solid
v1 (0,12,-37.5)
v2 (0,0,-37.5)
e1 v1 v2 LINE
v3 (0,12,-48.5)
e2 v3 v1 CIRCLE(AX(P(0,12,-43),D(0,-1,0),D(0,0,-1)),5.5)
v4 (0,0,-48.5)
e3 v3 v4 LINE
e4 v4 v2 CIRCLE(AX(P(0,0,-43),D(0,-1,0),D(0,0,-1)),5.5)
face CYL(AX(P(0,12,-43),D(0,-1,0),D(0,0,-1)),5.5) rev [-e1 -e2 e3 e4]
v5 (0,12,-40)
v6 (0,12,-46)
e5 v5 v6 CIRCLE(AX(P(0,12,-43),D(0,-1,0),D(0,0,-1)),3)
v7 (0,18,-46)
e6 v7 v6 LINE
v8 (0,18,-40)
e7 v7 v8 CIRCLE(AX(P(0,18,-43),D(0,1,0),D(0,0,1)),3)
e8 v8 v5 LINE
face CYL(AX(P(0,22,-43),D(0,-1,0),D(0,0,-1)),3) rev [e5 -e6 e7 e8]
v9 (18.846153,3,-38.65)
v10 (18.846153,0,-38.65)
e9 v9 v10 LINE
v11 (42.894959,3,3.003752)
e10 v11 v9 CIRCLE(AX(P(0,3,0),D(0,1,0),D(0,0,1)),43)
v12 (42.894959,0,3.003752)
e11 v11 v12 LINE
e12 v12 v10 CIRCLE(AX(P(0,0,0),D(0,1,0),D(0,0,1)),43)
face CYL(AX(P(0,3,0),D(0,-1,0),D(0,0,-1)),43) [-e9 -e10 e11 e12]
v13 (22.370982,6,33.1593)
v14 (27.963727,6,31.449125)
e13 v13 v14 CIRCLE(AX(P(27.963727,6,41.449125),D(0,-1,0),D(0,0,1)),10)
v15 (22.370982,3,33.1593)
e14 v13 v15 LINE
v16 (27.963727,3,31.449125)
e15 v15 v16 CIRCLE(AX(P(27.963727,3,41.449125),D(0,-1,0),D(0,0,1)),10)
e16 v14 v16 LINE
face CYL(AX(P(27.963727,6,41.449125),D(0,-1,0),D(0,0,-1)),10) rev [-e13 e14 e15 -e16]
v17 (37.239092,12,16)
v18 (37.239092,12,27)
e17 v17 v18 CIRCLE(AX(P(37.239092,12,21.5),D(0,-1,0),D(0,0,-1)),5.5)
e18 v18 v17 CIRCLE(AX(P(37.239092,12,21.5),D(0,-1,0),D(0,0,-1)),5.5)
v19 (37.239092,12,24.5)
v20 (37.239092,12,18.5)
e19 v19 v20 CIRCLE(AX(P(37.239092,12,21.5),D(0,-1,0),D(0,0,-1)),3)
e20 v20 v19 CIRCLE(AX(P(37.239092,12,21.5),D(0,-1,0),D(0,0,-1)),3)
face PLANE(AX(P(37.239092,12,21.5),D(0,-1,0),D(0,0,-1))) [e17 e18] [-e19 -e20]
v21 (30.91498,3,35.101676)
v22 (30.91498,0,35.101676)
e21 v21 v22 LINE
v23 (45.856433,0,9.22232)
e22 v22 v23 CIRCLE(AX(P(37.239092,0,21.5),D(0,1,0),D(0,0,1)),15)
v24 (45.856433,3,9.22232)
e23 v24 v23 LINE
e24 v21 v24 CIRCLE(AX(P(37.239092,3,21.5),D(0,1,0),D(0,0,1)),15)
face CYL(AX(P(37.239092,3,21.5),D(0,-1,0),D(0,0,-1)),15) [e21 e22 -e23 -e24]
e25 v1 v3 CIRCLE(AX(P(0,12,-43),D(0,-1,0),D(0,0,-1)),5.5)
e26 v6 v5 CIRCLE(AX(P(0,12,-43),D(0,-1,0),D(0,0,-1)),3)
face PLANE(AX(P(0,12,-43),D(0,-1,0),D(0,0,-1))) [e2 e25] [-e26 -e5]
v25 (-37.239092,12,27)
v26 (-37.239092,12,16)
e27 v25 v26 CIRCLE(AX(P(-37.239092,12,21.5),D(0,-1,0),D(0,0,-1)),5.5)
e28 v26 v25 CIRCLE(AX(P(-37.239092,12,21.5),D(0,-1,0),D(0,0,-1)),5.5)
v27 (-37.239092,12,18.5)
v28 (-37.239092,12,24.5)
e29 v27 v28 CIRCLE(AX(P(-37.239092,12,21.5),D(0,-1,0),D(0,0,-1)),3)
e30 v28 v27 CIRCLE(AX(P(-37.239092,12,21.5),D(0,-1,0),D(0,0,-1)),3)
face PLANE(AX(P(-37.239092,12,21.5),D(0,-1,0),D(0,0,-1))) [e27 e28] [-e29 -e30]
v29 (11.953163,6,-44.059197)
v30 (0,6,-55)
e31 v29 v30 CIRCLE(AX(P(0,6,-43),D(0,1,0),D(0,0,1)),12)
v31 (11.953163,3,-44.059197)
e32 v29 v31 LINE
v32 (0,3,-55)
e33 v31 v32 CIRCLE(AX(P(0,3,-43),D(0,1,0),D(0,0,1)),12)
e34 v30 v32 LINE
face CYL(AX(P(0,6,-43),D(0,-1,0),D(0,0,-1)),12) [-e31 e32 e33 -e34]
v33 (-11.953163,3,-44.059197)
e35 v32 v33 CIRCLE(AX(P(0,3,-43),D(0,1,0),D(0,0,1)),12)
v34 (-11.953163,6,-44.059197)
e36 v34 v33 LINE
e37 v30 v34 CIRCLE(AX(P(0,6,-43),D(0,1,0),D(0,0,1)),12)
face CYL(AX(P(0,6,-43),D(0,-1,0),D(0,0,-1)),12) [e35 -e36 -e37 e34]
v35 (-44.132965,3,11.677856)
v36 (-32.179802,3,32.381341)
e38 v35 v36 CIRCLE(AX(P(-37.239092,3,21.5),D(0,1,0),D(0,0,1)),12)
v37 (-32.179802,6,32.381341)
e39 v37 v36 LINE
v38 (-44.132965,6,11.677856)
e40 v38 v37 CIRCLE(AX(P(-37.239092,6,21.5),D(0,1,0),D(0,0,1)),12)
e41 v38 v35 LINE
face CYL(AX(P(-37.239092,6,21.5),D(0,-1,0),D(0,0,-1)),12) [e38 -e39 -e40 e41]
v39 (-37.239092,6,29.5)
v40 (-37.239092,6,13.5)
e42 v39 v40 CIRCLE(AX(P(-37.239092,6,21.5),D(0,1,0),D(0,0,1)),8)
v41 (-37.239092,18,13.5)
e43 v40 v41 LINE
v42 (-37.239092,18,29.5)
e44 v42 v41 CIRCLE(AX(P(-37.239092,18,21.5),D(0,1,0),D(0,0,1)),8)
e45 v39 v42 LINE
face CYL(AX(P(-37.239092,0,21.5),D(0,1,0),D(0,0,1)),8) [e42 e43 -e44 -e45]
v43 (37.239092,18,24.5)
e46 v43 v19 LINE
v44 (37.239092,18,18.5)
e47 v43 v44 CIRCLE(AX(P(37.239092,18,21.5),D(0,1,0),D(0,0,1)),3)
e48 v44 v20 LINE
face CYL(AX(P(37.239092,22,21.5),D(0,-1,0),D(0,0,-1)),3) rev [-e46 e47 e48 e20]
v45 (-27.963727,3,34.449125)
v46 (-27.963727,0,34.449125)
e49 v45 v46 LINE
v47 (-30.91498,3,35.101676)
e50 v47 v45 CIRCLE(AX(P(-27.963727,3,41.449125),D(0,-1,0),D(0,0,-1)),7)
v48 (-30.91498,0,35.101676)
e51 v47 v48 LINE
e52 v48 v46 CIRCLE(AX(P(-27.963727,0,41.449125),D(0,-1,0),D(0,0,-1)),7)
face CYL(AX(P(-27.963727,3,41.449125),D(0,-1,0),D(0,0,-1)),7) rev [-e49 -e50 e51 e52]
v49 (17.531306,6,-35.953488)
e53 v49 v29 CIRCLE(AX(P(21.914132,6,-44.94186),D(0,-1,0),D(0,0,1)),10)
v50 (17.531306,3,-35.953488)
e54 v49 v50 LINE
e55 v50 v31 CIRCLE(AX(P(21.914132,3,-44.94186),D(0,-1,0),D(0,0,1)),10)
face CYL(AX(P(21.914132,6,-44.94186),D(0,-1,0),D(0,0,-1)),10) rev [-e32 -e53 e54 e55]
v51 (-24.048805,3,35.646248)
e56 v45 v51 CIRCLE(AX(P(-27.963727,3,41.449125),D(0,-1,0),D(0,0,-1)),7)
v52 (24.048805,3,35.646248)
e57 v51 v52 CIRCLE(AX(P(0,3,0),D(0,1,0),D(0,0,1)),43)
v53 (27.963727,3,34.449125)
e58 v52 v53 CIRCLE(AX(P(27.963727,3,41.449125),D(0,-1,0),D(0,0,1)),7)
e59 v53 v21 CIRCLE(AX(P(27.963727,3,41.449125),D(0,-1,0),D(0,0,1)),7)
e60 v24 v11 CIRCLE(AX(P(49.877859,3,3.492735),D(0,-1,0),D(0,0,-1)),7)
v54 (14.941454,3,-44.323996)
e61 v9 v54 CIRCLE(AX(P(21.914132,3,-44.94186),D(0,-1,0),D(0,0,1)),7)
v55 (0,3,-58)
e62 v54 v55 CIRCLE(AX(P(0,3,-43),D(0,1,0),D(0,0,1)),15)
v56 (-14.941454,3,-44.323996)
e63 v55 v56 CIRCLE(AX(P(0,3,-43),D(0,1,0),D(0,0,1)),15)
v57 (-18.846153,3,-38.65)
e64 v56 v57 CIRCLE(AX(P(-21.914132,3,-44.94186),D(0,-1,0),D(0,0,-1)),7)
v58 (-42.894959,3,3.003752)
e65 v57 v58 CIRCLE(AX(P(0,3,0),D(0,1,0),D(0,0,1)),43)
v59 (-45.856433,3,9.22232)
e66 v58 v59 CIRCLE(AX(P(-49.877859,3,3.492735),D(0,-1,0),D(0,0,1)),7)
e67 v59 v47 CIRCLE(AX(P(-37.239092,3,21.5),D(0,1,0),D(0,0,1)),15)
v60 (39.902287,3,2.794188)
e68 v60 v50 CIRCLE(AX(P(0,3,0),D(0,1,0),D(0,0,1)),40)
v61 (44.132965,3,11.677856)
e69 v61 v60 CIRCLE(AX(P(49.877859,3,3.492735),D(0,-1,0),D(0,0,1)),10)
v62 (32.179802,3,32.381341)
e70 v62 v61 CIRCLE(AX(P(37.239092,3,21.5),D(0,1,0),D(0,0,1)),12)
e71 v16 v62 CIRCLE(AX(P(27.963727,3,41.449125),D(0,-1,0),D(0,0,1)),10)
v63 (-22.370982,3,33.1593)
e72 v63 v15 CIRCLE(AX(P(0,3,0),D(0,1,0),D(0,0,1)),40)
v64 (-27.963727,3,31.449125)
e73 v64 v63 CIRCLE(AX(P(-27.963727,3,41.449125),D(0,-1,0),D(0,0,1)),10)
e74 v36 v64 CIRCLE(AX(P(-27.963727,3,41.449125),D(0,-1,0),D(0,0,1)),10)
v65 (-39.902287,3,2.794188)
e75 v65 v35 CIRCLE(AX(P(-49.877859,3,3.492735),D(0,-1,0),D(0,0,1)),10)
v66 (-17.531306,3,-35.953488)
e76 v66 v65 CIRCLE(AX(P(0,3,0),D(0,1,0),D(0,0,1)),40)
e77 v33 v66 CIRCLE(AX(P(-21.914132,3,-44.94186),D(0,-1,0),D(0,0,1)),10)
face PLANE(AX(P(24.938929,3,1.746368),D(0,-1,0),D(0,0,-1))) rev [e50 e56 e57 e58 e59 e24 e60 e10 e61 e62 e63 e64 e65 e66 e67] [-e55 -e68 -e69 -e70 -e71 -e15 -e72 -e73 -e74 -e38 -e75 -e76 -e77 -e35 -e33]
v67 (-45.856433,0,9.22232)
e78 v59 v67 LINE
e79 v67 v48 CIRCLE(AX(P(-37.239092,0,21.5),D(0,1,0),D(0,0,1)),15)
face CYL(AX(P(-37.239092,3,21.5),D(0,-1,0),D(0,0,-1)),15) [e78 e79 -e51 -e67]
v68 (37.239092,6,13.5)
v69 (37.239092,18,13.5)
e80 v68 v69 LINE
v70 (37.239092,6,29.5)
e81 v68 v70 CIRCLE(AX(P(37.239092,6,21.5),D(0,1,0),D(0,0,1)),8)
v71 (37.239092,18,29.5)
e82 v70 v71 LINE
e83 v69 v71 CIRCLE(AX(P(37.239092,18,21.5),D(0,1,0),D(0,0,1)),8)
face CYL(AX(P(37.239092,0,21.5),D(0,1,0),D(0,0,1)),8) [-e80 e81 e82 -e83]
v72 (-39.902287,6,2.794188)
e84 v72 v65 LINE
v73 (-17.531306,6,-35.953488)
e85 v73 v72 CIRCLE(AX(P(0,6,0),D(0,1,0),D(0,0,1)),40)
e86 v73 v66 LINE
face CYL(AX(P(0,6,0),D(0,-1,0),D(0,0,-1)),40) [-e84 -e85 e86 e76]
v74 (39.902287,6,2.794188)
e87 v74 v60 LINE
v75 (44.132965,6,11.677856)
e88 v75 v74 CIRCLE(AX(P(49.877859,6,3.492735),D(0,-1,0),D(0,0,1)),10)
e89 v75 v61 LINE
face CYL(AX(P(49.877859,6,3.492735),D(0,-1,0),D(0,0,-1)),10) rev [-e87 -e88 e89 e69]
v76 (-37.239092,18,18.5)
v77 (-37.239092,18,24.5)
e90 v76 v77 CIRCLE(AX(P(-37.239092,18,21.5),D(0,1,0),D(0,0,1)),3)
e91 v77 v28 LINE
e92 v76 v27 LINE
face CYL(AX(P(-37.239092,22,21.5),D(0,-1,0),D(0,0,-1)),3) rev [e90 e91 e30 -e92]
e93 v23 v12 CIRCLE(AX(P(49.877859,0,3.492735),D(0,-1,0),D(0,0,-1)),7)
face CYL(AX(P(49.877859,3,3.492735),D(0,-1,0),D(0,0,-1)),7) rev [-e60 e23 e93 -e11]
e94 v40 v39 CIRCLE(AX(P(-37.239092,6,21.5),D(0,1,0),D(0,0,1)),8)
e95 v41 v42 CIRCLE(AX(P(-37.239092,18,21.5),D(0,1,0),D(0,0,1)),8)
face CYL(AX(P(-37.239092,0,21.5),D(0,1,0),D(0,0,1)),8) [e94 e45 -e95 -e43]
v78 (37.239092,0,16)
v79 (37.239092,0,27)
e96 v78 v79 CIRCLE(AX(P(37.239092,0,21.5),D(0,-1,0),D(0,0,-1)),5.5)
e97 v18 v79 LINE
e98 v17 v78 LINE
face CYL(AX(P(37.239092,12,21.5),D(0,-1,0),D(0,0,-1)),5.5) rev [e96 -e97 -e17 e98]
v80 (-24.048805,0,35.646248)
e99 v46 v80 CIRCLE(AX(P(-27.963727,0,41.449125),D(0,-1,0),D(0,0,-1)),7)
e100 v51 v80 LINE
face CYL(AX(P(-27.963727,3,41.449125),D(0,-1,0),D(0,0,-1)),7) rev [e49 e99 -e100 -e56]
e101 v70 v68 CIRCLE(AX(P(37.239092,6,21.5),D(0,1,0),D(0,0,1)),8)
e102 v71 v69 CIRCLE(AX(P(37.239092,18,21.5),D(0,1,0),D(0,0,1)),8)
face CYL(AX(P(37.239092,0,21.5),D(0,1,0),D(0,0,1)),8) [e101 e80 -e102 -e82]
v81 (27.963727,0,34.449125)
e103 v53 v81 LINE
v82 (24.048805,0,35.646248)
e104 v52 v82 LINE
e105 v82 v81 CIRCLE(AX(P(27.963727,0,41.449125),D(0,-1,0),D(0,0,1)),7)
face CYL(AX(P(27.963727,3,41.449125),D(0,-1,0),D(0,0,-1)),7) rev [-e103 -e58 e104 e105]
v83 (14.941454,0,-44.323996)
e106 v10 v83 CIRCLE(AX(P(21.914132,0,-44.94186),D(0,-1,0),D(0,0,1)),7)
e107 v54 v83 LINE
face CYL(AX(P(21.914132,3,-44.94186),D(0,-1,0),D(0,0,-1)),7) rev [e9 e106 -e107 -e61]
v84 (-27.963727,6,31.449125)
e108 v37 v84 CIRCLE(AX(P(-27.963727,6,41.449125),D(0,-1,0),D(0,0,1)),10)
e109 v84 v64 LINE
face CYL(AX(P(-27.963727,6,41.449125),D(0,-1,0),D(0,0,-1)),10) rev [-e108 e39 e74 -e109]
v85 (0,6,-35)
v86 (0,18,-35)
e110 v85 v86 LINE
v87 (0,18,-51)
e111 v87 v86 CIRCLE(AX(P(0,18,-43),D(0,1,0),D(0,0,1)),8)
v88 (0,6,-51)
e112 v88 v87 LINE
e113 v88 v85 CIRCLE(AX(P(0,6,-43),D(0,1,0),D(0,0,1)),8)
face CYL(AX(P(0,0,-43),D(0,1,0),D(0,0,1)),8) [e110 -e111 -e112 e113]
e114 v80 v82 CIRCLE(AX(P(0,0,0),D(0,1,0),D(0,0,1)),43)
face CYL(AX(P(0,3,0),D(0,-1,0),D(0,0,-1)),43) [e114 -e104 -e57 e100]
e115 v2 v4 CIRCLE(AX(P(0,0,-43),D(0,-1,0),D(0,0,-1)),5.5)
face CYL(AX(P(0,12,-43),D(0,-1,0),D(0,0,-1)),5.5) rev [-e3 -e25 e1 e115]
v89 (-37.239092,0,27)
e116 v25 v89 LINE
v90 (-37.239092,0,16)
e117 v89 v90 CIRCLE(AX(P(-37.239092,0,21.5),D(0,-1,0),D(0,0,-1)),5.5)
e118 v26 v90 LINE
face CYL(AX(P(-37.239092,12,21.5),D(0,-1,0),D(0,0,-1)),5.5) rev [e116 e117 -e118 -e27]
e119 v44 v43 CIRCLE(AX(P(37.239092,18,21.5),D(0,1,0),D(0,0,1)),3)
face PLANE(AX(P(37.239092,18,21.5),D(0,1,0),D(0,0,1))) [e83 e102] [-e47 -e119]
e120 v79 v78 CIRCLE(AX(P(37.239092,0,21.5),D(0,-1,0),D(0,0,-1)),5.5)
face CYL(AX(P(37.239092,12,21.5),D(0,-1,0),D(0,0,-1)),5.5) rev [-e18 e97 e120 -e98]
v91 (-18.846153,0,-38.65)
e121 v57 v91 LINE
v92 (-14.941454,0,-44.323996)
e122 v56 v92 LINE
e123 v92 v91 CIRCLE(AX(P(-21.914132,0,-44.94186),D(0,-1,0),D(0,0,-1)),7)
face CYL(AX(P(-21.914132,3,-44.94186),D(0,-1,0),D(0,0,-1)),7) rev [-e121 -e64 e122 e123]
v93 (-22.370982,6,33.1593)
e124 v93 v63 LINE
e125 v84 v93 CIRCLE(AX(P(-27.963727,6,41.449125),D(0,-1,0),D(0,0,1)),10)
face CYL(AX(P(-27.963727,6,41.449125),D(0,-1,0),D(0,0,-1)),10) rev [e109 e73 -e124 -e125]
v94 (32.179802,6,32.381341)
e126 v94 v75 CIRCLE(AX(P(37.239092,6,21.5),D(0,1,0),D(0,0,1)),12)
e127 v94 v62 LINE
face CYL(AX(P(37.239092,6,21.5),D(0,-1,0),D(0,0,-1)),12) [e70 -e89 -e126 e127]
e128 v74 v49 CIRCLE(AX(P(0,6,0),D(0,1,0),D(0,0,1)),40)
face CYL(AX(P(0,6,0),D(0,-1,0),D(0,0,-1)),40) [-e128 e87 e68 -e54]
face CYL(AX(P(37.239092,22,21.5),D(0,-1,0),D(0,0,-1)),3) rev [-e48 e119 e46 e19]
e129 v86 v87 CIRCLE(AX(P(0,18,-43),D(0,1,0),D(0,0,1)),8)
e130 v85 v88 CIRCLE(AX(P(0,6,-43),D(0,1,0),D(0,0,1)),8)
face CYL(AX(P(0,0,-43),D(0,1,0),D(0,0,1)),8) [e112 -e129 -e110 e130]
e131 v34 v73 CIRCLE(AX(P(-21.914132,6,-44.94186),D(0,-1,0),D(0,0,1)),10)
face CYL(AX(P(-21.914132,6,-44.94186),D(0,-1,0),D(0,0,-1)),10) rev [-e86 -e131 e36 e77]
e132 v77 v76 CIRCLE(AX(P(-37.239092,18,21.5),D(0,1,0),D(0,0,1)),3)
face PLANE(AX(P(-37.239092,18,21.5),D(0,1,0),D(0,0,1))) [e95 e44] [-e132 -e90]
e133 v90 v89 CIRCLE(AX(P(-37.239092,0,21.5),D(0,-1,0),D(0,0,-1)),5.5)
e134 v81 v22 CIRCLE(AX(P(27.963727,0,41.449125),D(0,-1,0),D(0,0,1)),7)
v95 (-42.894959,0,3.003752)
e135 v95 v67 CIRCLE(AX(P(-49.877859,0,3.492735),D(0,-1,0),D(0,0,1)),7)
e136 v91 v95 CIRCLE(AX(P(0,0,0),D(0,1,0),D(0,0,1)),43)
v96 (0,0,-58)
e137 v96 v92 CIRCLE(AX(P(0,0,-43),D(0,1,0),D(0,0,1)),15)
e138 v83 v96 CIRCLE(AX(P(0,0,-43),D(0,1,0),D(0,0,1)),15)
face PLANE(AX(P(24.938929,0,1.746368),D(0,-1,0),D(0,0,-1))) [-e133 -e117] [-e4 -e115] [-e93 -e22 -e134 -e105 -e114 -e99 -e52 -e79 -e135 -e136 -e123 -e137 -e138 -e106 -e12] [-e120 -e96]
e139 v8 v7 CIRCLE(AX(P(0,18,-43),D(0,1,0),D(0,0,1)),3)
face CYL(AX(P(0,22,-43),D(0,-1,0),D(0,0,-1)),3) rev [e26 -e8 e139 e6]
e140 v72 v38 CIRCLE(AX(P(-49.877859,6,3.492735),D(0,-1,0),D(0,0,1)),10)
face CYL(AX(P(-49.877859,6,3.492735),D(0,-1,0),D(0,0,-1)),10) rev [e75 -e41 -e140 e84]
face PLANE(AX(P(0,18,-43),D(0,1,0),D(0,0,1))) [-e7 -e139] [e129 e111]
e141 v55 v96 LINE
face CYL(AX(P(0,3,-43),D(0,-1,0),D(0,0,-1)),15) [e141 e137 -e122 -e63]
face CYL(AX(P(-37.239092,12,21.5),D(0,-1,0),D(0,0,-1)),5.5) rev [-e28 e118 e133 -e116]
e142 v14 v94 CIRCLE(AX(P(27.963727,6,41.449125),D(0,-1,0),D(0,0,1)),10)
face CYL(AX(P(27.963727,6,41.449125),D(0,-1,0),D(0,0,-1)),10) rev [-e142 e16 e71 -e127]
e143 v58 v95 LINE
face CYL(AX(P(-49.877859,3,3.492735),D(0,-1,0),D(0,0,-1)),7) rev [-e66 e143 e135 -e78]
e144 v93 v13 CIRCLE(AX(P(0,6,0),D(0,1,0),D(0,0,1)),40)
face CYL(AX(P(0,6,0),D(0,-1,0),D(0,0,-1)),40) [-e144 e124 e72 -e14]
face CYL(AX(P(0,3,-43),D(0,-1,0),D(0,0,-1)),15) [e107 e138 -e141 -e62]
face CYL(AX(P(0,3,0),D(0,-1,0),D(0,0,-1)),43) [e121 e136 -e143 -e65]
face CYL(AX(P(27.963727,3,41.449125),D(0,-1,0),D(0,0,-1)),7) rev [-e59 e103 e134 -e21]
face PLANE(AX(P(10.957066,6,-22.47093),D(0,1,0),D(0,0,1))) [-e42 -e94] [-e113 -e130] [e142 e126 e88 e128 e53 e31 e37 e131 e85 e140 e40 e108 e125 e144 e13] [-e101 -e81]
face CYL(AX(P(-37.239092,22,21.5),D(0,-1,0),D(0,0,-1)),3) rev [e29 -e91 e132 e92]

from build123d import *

# Parameters (mm, degrees)
BASE_FLANGE_PROFILE_R     = 8
BASE_FLANGE_3MM_DEPTH     = 3
RAISED_PLATE_3MM_DEPTH    = 3
LOBE_CUT_PROFILE_3X_R     = 8
LOBE_CUT_3X_13MM_DEPTH    = 13
BOSSES_3X_DEPTH           = 12
BOSSES_3X_DEPTH_BACK      = 6
BOSS_PROFILE_3X_R         = 8
BOSS_HOLE_PROFILE_3X_R    = 5.5
BOSS_HOLE_PROFILE_3X_R_2  = 3
BOSS_HOLES_3X_12MM_DEPTH  = 12
THROUGH_CUT_PROFILE_3X_R  = 3
THROUGH_CUT_3X_22MM_DEPTH = 22


with BuildPart() as part:
    # Base Flange Profile → Base Flange 3mm (new body)
    with BuildSketch(Plane(origin=(0, 0, 0), x_dir=(1, 0, 0), z_dir=(0, 1, 0))):
        with BuildLine():
            ThreePointArc((14.941453584, 44.323995772), (0, 58), (-14.941453584, 44.323995772))
            ThreePointArc((-14.941453584, 44.323995772), (-16.147655157, 40.973517523), (-18.846153454, 38.65))
            ThreePointArc((-18.846153454, 38.65), (-37.239092363, 21.5), (-42.894958583, -3.003752345))
            ThreePointArc((-42.894958583, -3.003752345), (-43.557934635, -6.502479184), (-45.856433127, -9.222319513))
            ThreePointArc((-45.856433127, -9.222319513), (-50.229473419, -29), (-30.914979544, -35.101676259))
            ThreePointArc((-30.914979544, -35.101676259), (-27.410279478, -34.471038339), (-24.048805129, -35.646247655))
            ThreePointArc((-24.048805129, -35.646247655), (0, -43), (24.048805129, -35.646247655))
            ThreePointArc((24.048805129, -35.646247655), (27.410279478, -34.471038339), (30.914979544, -35.101676259))
            ThreePointArc((30.914979544, -35.101676259), (50.229473419, -29), (45.856433127, -9.222319513))
            ThreePointArc((45.856433127, -9.222319513), (43.557934635, -6.502479184), (42.894958583, -3.003752345))
            ThreePointArc((42.894958583, -3.003752345), (37.239092363, 21.5), (18.846153454, 38.65))
            ThreePointArc((18.846153454, 38.65), (16.147655157, 40.973517523), (14.941453584, 44.323995772))
        make_face()
        with Locations(Location((0, 43, 0), (0, 0, 270))):
            Circle(BASE_FLANGE_PROFILE_R, mode=Mode.SUBTRACT)
        with Locations(Location((37.239092363, -21.5, 0), (0, 0, 270))):
            Circle(BASE_FLANGE_PROFILE_R, mode=Mode.SUBTRACT)
        with Locations(Location((-37.239092363, -21.5, 0), (0, 0, 270))):
            Circle(BASE_FLANGE_PROFILE_R, mode=Mode.SUBTRACT)
    extrude(amount=BASE_FLANGE_3MM_DEPTH)

    # Raised Plate Profile → Raised Plate 3mm (add)
    with BuildSketch(Plane(origin=(0, 3, 0), x_dir=(1, 0, 0), z_dir=(0, 1, 0))):
        with BuildLine():
            ThreePointArc((39.902287054, -2.794188228), (40.8493957, -7.792369426), (44.132964974, -11.67785561))
            ThreePointArc((44.132964974, -11.67785561), (47.631397208, -27.5), (32.179802107, -32.381341007))
            ThreePointArc((32.179802107, -32.381341007), (27.173087728, -31.480429693), (22.370981516, -33.159300144))
            ThreePointArc((22.370981516, -33.159300144), (0, -40), (-22.370981516, -33.159300144))
            ThreePointArc((-22.370981516, -33.159300144), (-27.173087728, -31.480429693), (-32.179802107, -32.381341007))
            ThreePointArc((-32.179802107, -32.381341007), (-47.631397208, -27.5), (-44.132964974, -11.67785561))
            ThreePointArc((-44.132964974, -11.67785561), (-40.8493957, -7.792369426), (-39.902287054, -2.794188228))
            ThreePointArc((-39.902287054, -2.794188228), (-34.641016151, 20), (-17.531305538, 35.953488372))
            ThreePointArc((-17.531305538, 35.953488372), (-13.676307972, 39.272799119), (-11.953162867, 44.059196617))
            ThreePointArc((-11.953162867, 44.059196617), (0, 55), (11.953162867, 44.059196617))
            ThreePointArc((11.953162867, 44.059196617), (13.676307972, 39.272799119), (17.531305538, 35.953488372))
            ThreePointArc((17.531305538, 35.953488372), (34.641016151, 20), (39.902287054, -2.794188228))
        make_face()
    extrude(amount=RAISED_PLATE_3MM_DEPTH)

    # Lobe Cut Profile 3x → Lobe Cut 3x 13mm (cut)
    with BuildSketch(Plane.XZ):
        with Locations(Location((0, -43, 0), (0, 0, 90))):
            Circle(LOBE_CUT_PROFILE_3X_R)
        with Locations(Location((37.239092363, 21.5, 0), (0, 0, 90))):
            Circle(LOBE_CUT_PROFILE_3X_R)
        with Locations(Location((-37.239092363, 21.5, 0), (0, 0, 90))):
            Circle(LOBE_CUT_PROFILE_3X_R)
    extrude(amount=-LOBE_CUT_3X_13MM_DEPTH, mode=Mode.SUBTRACT)

    # Boss Profile 3x → Bosses 3x (add, two sides: drawn at the far end of the back side and taken through both)
    with BuildSketch(Plane(origin=(0, 6, 0), x_dir=(1, 0, 0), z_dir=(0, 1, 0)).offset(-BOSSES_3X_DEPTH_BACK)):
        with Locations(Location((0, 43, 0), (0, 0, 270))):
            Circle(BOSS_PROFILE_3X_R)
        with Locations(Location((37.239092363, -21.5, 0), (0, 0, 270))):
            Circle(BOSS_PROFILE_3X_R)
        with Locations(Location((-37.239092363, -21.5, 0), (0, 0, 270))):
            Circle(BOSS_PROFILE_3X_R)
    extrude(amount=BOSSES_3X_DEPTH + BOSSES_3X_DEPTH_BACK)

    # Boss Hole Profile 3x → Boss Holes 3x 12mm (cut)
    # profile 1 of 3: a face of its own
    with BuildSketch(Plane.XZ):
        with Locations(Location((0, -43, 0), (0, 0, 270))):
            Circle(BOSS_HOLE_PROFILE_3X_R)
        with Locations(Location((0, -43, 0), (0, 0, 270))):
            Circle(BOSS_HOLE_PROFILE_3X_R_2, mode=Mode.SUBTRACT)
    # profile 2 of 3: a face of its own
    with BuildSketch(Plane.XZ):
        with Locations(Location((37.239092363, 21.5, 0), (0, 0, 270))):
            Circle(BOSS_HOLE_PROFILE_3X_R)
        with Locations(Location((37.239092363, 21.5, 0), (0, 0, 270))):
            Circle(BOSS_HOLE_PROFILE_3X_R_2, mode=Mode.SUBTRACT)
    # profile 3 of 3: a face of its own
    with BuildSketch(Plane.XZ):
        with Locations(Location((-37.239092363, 21.5, 0), (0, 0, 270))):
            Circle(BOSS_HOLE_PROFILE_3X_R)
        with Locations(Location((-37.239092363, 21.5, 0), (0, 0, 270))):
            Circle(BOSS_HOLE_PROFILE_3X_R_2, mode=Mode.SUBTRACT)
    extrude(amount=-BOSS_HOLES_3X_12MM_DEPTH, mode=Mode.SUBTRACT)

    # Through Cut Profile 3x → Through Cut 3x 22mm (cut)
    with BuildSketch(Plane.XZ):
        with Locations(Location((0, -43, 0), (0, 0, 270))):
            Circle(THROUGH_CUT_PROFILE_3X_R)
        with Locations(Location((37.239092363, 21.5, 0), (0, 0, 270))):
            Circle(THROUGH_CUT_PROFILE_3X_R)
        with Locations(Location((-37.239092363, 21.5, 0), (0, 0, 270))):
            Circle(THROUGH_CUT_PROFILE_3X_R)
    extrude(amount=-THROUGH_CUT_3X_22MM_DEPTH, mode=Mode.SUBTRACT)


solid = part.part
